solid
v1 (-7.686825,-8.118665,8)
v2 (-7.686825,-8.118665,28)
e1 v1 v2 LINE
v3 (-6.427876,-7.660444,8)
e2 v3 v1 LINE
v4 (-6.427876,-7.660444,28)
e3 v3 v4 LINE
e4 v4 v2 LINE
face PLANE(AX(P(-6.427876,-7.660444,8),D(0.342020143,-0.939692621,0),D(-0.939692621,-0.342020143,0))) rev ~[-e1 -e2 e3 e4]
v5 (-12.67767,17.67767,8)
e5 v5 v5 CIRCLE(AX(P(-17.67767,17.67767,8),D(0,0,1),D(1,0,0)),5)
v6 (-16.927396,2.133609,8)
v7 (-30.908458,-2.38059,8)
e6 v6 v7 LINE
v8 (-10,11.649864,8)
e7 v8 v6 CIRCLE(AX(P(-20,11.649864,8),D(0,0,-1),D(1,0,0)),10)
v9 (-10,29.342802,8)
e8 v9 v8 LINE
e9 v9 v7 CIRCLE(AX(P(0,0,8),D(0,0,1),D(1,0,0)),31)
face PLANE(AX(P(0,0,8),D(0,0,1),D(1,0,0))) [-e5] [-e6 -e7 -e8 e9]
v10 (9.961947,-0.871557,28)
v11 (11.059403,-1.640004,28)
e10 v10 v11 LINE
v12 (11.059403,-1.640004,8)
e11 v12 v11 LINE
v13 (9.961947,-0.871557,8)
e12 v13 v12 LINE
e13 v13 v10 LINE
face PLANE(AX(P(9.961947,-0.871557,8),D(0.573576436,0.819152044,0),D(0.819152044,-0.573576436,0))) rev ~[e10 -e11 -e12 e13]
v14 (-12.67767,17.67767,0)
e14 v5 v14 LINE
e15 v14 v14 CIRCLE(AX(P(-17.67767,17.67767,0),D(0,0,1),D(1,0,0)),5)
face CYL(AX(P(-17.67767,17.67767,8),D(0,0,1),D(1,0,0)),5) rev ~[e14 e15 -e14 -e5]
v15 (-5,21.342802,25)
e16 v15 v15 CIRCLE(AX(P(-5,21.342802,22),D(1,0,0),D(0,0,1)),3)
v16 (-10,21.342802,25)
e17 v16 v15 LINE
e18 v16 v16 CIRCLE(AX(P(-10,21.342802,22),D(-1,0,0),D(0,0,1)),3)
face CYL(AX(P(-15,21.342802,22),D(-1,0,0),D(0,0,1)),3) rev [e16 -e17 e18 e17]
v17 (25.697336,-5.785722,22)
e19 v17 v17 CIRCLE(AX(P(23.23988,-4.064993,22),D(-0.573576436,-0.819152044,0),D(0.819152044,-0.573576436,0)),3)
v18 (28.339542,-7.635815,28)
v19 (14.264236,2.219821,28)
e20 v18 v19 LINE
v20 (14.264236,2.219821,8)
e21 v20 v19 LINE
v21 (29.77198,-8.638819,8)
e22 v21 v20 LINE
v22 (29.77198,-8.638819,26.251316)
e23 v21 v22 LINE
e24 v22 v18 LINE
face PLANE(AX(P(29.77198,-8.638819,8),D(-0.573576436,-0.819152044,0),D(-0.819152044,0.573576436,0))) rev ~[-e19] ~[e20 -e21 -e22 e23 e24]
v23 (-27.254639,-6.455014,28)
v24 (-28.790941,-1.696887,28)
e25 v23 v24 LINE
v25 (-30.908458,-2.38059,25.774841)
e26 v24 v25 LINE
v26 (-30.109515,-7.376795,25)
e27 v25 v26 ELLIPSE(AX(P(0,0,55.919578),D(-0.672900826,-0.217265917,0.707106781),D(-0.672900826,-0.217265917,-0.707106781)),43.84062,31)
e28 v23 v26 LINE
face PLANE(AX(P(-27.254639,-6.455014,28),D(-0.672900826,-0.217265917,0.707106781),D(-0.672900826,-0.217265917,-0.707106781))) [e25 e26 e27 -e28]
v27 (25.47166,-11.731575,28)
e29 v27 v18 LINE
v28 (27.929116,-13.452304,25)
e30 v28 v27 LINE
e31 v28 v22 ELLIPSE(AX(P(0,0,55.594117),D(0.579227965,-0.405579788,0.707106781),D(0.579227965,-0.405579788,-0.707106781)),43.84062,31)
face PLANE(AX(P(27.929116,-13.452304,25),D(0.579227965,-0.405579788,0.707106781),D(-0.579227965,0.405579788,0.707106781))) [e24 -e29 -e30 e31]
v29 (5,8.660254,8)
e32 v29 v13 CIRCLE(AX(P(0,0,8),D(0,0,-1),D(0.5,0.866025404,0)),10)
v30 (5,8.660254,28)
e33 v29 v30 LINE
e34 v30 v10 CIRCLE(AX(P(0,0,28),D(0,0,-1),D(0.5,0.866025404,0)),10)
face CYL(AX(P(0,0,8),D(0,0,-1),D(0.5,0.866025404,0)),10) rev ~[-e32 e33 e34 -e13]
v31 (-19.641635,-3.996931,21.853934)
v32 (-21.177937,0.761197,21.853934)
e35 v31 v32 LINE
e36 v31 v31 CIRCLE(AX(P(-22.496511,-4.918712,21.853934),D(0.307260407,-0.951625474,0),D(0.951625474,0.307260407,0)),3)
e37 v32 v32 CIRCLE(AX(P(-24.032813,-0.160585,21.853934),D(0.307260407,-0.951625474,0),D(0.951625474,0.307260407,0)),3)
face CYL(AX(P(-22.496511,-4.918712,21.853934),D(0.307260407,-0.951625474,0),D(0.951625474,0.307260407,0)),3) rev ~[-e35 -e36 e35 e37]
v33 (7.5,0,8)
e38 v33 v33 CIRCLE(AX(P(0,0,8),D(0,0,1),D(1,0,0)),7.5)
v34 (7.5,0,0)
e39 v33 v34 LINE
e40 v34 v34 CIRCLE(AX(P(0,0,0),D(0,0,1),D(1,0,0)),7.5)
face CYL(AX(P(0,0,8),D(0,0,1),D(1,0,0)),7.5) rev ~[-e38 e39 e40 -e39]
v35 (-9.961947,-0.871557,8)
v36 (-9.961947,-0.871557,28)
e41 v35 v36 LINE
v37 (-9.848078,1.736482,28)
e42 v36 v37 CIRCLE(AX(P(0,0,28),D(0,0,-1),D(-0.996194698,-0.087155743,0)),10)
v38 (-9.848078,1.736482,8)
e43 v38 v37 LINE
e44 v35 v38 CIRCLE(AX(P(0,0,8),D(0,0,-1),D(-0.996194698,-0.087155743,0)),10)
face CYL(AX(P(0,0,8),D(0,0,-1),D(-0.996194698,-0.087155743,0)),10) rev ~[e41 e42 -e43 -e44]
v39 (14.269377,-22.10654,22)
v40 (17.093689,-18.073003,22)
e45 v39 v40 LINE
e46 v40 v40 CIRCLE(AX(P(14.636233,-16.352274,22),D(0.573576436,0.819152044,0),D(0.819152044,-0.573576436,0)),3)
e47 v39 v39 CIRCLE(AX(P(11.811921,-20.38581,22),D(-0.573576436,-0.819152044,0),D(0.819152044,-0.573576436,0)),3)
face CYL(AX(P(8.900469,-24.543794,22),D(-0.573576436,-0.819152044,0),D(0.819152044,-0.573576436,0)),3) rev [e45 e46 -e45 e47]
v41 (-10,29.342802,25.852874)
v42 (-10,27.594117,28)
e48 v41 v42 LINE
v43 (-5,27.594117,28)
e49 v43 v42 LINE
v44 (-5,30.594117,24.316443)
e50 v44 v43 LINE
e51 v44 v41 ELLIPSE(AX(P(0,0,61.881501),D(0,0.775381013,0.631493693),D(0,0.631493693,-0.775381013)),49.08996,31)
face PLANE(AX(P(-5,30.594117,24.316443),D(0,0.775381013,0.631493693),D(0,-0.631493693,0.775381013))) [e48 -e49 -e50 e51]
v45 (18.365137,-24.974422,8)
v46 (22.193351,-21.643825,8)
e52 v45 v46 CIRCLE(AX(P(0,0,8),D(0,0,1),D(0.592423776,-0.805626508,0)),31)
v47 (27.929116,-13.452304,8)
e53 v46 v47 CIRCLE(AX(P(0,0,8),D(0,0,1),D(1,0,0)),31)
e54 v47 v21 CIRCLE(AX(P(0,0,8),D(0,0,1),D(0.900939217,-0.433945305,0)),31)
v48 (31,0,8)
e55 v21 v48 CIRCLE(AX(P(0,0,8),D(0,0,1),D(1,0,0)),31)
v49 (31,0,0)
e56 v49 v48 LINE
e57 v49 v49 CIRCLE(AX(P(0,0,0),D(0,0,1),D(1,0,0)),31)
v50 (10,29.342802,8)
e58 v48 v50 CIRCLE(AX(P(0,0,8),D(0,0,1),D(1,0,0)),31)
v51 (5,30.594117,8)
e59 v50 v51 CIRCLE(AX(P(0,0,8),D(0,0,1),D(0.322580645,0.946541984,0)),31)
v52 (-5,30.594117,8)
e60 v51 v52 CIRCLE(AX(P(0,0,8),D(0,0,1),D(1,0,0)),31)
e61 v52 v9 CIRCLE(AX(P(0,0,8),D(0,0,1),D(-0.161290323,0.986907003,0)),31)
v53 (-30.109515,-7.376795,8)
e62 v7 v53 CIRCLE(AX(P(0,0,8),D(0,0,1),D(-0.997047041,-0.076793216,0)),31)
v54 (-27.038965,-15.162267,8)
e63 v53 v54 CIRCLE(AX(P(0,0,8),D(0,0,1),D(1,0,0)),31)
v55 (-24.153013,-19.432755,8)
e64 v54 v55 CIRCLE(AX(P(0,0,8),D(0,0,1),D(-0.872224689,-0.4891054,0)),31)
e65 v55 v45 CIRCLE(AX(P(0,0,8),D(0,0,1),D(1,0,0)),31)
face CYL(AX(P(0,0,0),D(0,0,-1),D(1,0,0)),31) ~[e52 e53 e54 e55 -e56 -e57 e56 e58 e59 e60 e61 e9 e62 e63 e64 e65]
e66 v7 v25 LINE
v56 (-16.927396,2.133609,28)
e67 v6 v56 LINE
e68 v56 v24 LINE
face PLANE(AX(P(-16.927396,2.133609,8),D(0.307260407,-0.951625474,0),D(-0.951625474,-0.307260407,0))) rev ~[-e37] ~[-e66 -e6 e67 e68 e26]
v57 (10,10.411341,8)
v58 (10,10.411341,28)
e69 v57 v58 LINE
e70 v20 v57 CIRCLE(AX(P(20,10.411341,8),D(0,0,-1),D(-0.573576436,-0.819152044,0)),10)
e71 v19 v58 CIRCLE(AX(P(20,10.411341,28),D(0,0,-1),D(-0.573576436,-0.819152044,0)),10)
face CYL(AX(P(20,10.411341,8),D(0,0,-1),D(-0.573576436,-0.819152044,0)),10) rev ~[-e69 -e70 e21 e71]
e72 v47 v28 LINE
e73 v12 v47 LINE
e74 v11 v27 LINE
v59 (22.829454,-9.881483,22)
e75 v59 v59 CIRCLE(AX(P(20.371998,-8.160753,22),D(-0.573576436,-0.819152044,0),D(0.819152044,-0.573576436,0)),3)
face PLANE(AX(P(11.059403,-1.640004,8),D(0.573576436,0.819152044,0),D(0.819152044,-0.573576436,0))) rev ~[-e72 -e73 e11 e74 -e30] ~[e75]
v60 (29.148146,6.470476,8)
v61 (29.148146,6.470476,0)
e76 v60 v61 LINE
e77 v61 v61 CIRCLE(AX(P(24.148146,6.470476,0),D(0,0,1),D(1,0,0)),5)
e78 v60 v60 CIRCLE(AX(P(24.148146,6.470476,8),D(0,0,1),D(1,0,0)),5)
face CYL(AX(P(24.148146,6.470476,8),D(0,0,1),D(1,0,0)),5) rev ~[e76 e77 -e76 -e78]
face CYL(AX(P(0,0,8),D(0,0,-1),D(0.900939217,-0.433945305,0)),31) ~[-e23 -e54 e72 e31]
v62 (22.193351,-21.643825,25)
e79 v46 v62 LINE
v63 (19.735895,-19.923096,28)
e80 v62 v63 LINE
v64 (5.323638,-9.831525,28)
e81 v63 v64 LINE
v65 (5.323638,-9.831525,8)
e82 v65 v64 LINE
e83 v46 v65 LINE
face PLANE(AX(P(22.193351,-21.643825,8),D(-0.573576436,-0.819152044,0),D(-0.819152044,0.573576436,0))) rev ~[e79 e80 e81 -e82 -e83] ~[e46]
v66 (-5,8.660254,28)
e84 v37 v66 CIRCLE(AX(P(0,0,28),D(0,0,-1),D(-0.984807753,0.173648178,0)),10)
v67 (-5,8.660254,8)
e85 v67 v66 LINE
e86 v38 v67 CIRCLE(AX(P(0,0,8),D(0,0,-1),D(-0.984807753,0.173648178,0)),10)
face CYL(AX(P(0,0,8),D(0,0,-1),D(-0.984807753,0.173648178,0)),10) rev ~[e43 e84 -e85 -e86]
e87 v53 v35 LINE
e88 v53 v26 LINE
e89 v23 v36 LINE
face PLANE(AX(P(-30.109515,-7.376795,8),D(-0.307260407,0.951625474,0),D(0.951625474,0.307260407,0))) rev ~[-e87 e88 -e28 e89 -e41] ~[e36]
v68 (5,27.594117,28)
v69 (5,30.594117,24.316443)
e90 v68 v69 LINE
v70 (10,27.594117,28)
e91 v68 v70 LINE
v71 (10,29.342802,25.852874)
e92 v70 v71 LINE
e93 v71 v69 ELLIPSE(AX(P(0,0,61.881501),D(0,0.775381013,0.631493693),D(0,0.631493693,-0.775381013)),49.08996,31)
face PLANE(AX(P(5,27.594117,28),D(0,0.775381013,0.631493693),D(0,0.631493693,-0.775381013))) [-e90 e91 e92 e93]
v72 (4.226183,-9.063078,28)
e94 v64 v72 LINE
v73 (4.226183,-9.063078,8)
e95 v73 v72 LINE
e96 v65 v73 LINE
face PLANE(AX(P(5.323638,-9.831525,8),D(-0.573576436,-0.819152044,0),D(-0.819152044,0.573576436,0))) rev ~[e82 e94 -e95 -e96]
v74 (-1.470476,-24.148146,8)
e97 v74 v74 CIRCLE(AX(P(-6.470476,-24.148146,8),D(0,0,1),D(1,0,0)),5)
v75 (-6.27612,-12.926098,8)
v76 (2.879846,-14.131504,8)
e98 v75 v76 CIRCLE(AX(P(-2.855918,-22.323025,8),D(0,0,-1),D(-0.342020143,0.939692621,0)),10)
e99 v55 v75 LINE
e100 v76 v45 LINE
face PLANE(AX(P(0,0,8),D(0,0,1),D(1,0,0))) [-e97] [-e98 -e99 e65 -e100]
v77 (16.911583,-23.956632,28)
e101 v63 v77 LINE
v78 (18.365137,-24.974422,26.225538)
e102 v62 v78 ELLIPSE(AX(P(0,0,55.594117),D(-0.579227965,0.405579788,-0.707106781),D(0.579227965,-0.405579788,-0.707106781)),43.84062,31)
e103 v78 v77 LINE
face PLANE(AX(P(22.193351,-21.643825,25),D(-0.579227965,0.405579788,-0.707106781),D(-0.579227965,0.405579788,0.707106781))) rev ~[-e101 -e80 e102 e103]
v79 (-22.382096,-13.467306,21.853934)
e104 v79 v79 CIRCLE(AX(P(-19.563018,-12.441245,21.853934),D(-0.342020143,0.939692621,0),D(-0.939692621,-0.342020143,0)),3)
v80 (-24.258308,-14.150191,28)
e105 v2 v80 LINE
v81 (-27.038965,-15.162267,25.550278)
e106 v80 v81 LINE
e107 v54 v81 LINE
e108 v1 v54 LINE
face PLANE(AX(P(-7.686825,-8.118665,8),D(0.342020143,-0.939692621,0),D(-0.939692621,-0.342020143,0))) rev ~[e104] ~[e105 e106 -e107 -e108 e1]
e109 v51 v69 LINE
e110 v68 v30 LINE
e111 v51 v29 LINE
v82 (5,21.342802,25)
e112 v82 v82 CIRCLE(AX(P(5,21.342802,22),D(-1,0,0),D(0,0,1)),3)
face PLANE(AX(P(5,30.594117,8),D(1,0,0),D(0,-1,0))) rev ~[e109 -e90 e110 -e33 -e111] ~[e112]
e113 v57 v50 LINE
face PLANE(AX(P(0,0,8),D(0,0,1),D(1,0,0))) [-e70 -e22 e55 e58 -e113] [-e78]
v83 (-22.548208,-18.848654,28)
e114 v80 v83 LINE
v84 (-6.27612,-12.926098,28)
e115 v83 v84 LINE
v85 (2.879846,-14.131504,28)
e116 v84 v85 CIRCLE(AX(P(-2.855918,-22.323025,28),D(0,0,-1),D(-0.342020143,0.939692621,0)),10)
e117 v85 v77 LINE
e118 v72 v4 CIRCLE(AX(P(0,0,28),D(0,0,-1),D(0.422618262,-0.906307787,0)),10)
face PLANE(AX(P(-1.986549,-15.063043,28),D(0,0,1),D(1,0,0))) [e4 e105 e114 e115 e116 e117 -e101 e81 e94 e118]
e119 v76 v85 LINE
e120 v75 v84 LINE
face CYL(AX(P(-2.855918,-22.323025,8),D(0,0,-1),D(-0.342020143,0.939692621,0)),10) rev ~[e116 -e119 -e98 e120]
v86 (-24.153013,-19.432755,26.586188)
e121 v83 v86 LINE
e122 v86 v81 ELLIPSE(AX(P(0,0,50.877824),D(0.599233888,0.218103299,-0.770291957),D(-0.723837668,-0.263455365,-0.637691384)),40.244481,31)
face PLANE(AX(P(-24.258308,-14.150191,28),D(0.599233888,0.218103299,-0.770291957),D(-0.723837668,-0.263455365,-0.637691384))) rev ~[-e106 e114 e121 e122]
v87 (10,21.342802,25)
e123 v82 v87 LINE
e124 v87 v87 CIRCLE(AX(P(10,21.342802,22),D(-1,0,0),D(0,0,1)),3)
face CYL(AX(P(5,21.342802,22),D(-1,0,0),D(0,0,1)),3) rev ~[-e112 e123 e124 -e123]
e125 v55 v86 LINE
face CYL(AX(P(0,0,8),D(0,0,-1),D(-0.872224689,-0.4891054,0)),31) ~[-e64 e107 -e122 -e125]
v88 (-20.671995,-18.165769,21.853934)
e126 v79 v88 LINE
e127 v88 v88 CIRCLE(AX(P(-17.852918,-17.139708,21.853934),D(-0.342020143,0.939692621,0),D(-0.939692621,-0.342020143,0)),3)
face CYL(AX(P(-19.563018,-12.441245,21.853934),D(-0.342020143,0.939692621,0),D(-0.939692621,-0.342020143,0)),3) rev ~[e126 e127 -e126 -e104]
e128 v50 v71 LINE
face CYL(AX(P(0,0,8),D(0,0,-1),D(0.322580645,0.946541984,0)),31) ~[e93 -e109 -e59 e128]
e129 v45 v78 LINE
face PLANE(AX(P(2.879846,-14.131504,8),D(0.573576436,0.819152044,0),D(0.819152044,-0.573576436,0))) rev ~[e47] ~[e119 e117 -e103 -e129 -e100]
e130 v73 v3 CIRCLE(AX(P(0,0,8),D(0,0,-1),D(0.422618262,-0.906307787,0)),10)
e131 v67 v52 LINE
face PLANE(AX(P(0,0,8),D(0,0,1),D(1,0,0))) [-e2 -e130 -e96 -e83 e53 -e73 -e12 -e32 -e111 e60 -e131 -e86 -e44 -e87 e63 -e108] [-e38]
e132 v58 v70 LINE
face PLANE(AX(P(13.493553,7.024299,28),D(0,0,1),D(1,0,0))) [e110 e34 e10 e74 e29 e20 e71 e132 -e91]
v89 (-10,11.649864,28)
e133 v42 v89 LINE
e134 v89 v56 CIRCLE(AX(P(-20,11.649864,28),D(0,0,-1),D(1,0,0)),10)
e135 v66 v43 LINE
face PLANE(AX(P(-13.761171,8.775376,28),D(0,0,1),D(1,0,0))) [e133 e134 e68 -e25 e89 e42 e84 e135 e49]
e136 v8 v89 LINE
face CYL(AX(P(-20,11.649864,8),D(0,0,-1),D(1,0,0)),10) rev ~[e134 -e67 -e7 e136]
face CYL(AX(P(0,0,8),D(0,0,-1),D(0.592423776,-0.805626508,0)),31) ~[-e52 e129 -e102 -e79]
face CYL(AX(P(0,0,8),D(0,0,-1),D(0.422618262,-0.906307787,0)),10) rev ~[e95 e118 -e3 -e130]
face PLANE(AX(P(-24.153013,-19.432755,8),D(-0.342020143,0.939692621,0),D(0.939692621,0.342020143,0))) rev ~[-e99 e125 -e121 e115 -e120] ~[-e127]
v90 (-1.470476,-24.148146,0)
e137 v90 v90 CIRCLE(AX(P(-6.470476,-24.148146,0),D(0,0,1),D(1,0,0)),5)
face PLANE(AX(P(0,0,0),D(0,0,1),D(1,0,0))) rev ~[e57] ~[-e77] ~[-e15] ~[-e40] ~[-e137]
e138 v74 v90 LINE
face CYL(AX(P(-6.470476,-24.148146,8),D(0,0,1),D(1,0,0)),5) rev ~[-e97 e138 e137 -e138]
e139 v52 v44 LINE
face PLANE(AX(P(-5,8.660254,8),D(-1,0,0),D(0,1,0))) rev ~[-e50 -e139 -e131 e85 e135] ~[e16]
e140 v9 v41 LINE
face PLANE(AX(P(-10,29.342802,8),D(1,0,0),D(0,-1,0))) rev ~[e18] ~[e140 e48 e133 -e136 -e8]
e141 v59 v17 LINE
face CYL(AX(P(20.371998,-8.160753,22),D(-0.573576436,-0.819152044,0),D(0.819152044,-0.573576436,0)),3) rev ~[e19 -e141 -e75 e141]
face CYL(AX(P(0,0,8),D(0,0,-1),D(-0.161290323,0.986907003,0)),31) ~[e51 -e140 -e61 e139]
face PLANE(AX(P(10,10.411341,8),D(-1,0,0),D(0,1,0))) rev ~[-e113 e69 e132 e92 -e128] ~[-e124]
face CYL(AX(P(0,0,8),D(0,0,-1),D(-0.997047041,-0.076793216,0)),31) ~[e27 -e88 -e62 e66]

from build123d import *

# Parameters (mm, degrees)
BASE_DISC_SKETCH_R     = 31
BASE_DISC_62_DEPTH     = 8
SQUARE_CUT_SKETCH_R    = 5
SQUARE_CUT_10X10_DEPTH = 8
JAWS_DEPTH             = 20
JAW_NOTCH_1_DEPTH      = 10
JAW_NOTCH_2_DEPTH      = 10
JAW_NOTCH_3_DEPTH      = 10
JAW_NOTCH_4_DEPTH      = 10
JAW_NOTCH_5_DEPTH      = 10
JAW_NOTCH_6_DEPTH      = 10
JAW_HOLE_1_SKETCH_R    = 3
JAW_HOLE_1_6_DEPTH     = 10
JAW_HOLE_2_SKETCH_R    = 3
JAW_HOLE_2_6_DEPTH     = 10
JAW_HOLE_3_SKETCH_R    = 3
JAW_HOLE_3_6_DEPTH     = 10
JAW_START              = -10
JAW_HOLE_4_SKETCH_R    = 3
JAW_HOLE_4_6_DEPTH     = 10
JAW_HOLE_5_SKETCH_R    = 3
JAW_HOLE_5_6_DEPTH     = 10
JAW_HOLE_6_SKETCH_R    = 3
JAW_HOLE_6_6_DEPTH     = 10
HOLE_15_SKETCH_R       = 7.5
HOLE_15_DEPTH          = 10


with BuildPart() as part:
    # Base Disc Sketch → Base Disc Ø62 (new body)
    with BuildSketch(Plane.XY):
        Circle(BASE_DISC_SKETCH_R)
    extrude(amount=BASE_DISC_62_DEPTH)

    # Square Cut Sketch → Square Cut 10x10 (cut)
    with BuildSketch(Plane.XY.offset(8)):
        with Locations((-17.67766953, 17.67766953)):
            Circle(SQUARE_CUT_SKETCH_R)
        with Locations((24.148145657, 6.470476128)):
            Circle(SQUARE_CUT_SKETCH_R)
        with Locations((-6.470476128, -24.148145657)):
            Circle(SQUARE_CUT_SKETCH_R)
    extrude(amount=-SQUARE_CUT_10X10_DEPTH, mode=Mode.SUBTRACT)

    # Jaws Sketch → Jaws (add)
    with BuildSketch(Plane.XY.offset(8)):
        with BuildLine():
            Line((-30.109514993, -7.376795165), (-9.961946981, -0.871557427))
            ThreePointArc((-9.961946981, -0.871557427), (-9.990482216, 0.436193874), (-9.84807753, 1.736481777))
            ThreePointArc((-9.84807753, 1.736481777), (-8.191520443, 5.735764364), (-5, 8.660254038))
            Line((-5, 8.660254038), (-5, 10))
            Line((-5, 10), (-5, 30.594117082))
            ThreePointArc((-5, 30.594117082), (-7.526051267, 30.072554802), (-10, 29.342801502))
            Line((-10, 29.342801502), (-10, 11.649864154))
            ThreePointArc((-10, 11.649864154), (-11.915260032, 5.764545161), (-16.927395931, 2.133609416))
            Line((-16.927395931, 2.133609416), (-30.908458268, -2.38058973))
            ThreePointArc((-30.908458268, -2.38058973), (-30.611089207, -4.895019672), (-30.109514993, -7.376795165))
        make_face()
        with BuildLine():
            ThreePointArc((4.226182617, -9.06307787), (-1.305261922, -9.914448614), (-6.427876097, -7.660444431))
            Line((-6.427876097, -7.660444431), (-7.686825491, -8.118664537))
            Line((-7.686825491, -8.118664537), (-27.038965344, -15.162267413))
            ThreePointArc((-27.038965344, -15.162267413), (-25.684896703, -17.357594343), (-24.153012612, -19.432755383))
            Line((-24.153012612, -19.432755383), (-6.276119738, -12.926098496))
            ThreePointArc((-6.276119738, -12.926098496), (-1.550656383, -12.40857609), (2.879846058, -14.131504261))
            Line((2.879846058, -14.131504261), (18.365137045, -24.974421741))
            ThreePointArc((18.365137045, -24.974421741), (20.347505117, -23.387582934), (22.193351369, -21.64382487))
            Line((22.193351369, -21.64382487), (5.323638261, -9.831524585))
            Line((5.323638261, -9.831524585), (4.226182617, -9.06307787))
        make_face()
        with BuildLine():
            ThreePointArc((10, 29.342801502), (7.526051267, 30.072554802), (5, 30.594117082))
            Line((5, 30.594117082), (5, 10))
            Line((5, 10), (5, 8.660254038))
            ThreePointArc((5, 8.660254038), (8.870108332, 4.617486132), (9.961946981, -0.871557427))
            Line((9.961946981, -0.871557427), (11.059402625, -1.640004142))
            Line((11.059402625, -1.640004142), (27.929115732, -13.452304428))
            ThreePointArc((27.929115732, -13.452304428), (28.950760409, -11.083928535), (29.771980199, -8.638819075))
            Line((29.771980199, -8.638819075), (14.264235636, 2.219820568))
            ThreePointArc((14.264235636, 2.219820568), (11.129891668, 5.793854879), (10, 10.411341011))
            Line((10, 10.411341011), (10, 29.342801502))
        make_face()
    extrude(amount=JAWS_DEPTH)

    # Jaw Notch 1 Sketch → Jaw Notch 1 (cut)
    with BuildSketch(Plane.ZY.offset(-5)):
        Polygon((28, 30.594117082), (28, 27.594117082), (24.316442961, 30.594117082), align=None)
    extrude(amount=-JAW_NOTCH_1_DEPTH, mode=Mode.SUBTRACT)

    # Jaw Notch 2 Sketch → Jaw Notch 2 (cut)
    with BuildSketch(Plane(origin=(-5, 0, 0), x_dir=(0, 0, -1), z_dir=(1, 0, 0))):
        Polygon((-28, 30.594117082), (-24.316442961, 30.594117082), (-28, 27.594117082), align=None)
    extrude(amount=-JAW_NOTCH_2_DEPTH, mode=Mode.SUBTRACT)

    # Jaw Notch 3 Sketch → Jaw Notch 3 (cut)
    with BuildSketch(Plane(origin=(2.867882182, 4.095760221, 0), x_dir=(0.8191520442889944, -0.5735764363510426, 0), z_dir=(-0.5735764363510426, -0.8191520442889944, 0))):
        Polygon((30.594117082, 28), (30.594117082, 25), (27.594117082, 28), align=None)
    extrude(amount=-JAW_NOTCH_3_DEPTH, mode=Mode.SUBTRACT)

    # Jaw Notch 4 Sketch → Jaw Notch 4 (cut)
    with BuildSketch(Plane(origin=(-2.867882182, -4.095760221, 0), x_dir=(0.8191520442889944, -0.5735764363510426, 0), z_dir=(0.5735764363510426, 0.8191520442889944, 0))):
        Polygon((27.594117082, -28), (30.594117082, -28), (30.594117082, -25), align=None)
    extrude(amount=-JAW_NOTCH_4_DEPTH, mode=Mode.SUBTRACT)

    # Jaw Notch 5 Sketch → Jaw Notch 5 (cut)
    with BuildSketch(Plane(origin=(-0.685656401, 2.123567121, 0), x_dir=(0.9516254737982698, 0.3072604068509618, 0), z_dir=(0.3072604068509618, -0.9516254737982698, 0))):
        Polygon((-30.919578554, 28), (-27.919578554, 28), (-30.919578554, 25), align=None)
    extrude(amount=-JAW_NOTCH_5_DEPTH, mode=Mode.SUBTRACT)

    # Jaw Notch 6 Sketch → Jaw Notch 6 (cut)
    with BuildSketch(Plane(origin=(1.710100717, -4.698463104, 0), x_dir=(0.9396926207859072, 0.34202014332567215, 0), z_dir=(-0.3420201433256721, 0.9396926207859071, 0))):
        Polygon((-27.635003822, -28), (-30.594117082, -25.550278158), (-30.594117082, -28), align=None)
    extrude(amount=-JAW_NOTCH_6_DEPTH, mode=Mode.SUBTRACT)

    # Jaw Hole 1 Sketch → Jaw Hole 1 Ø6 (cut)
    with BuildSketch(Plane(origin=(-0.685656401, 2.123567121, 0), x_dir=(0.9516254737982698, 0.3072604068509618, 0), z_dir=(0.3072604068509618, -0.9516254737982698, 0))):
        with Locations((-22.919578554, 21.853934113)):
            Circle(JAW_HOLE_1_SKETCH_R)
    extrude(amount=-JAW_HOLE_1_6_DEPTH, mode=Mode.SUBTRACT)

    # Jaw Hole 2 Sketch → Jaw Hole 2 Ø6 (cut)
    with BuildSketch(Plane(origin=(1.710100717, -4.698463104, 0), x_dir=(0.9396926207859072, 0.34202014332567215, 0), z_dir=(-0.3420201433256721, 0.9396926207859071, 0))):
        with Locations(Location((-22.638380403, -21.853934113, 0), (0, 0, 180))):
            Circle(JAW_HOLE_2_SKETCH_R)
    extrude(amount=-JAW_HOLE_2_6_DEPTH, mode=Mode.SUBTRACT)

    # Jaw Hole 3 Sketch → Jaw Hole 3 Ø6 (cut)
    with BuildSketch(Plane.ZY.offset(-5)):
        with Locations((22, 21.342801502)):
            Circle(JAW_HOLE_3_SKETCH_R)
    extrude(amount=-JAW_HOLE_3_6_DEPTH, mode=Mode.SUBTRACT)

    # Jaw Hole 4 Sketch → Jaw Hole 4 Ø6 (cut)
    with BuildSketch(Plane(origin=(-5, 0, 0), x_dir=(0, 0, -1), z_dir=(1, 0, 0)).offset(JAW_START)):
        with Locations(Location((-22, 21.342801502, 0), (0, 0, 180))):
            Circle(JAW_HOLE_4_SKETCH_R)
    extrude(amount=JAW_HOLE_4_6_DEPTH, mode=Mode.SUBTRACT)

    # Jaw Hole 5 Sketch → Jaw Hole 5 Ø6 (cut)
    with BuildSketch(Plane(origin=(2.867882182, 4.095760221, 0), x_dir=(0.8191520442889944, -0.5735764363510426, 0), z_dir=(-0.5735764363510426, -0.8191520442889944, 0))):
        with Locations((21.368579376, 22)):
            Circle(JAW_HOLE_5_SKETCH_R)
    extrude(amount=-JAW_HOLE_5_6_DEPTH, mode=Mode.SUBTRACT)

    # Jaw Hole 6 Sketch → Jaw Hole 6 Ø6 (cut)
    with BuildSketch(Plane(origin=(-2.867882182, -4.095760221, 0), x_dir=(0.8191520442889944, -0.5735764363510426, 0), z_dir=(0.5735764363510426, 0.8191520442889944, 0)).offset(JAW_START)):
        with Locations((21.368579376, -22)):
            Circle(JAW_HOLE_6_SKETCH_R)
    extrude(amount=JAW_HOLE_6_6_DEPTH, mode=Mode.SUBTRACT)

    # Hole Ø15 Sketch → Hole Ø15 (cut)
    with BuildSketch(Plane.XY.offset(8)):
        Circle(HOLE_15_SKETCH_R)
    extrude(amount=-HOLE_15_DEPTH, mode=Mode.SUBTRACT)


solid = part.part
